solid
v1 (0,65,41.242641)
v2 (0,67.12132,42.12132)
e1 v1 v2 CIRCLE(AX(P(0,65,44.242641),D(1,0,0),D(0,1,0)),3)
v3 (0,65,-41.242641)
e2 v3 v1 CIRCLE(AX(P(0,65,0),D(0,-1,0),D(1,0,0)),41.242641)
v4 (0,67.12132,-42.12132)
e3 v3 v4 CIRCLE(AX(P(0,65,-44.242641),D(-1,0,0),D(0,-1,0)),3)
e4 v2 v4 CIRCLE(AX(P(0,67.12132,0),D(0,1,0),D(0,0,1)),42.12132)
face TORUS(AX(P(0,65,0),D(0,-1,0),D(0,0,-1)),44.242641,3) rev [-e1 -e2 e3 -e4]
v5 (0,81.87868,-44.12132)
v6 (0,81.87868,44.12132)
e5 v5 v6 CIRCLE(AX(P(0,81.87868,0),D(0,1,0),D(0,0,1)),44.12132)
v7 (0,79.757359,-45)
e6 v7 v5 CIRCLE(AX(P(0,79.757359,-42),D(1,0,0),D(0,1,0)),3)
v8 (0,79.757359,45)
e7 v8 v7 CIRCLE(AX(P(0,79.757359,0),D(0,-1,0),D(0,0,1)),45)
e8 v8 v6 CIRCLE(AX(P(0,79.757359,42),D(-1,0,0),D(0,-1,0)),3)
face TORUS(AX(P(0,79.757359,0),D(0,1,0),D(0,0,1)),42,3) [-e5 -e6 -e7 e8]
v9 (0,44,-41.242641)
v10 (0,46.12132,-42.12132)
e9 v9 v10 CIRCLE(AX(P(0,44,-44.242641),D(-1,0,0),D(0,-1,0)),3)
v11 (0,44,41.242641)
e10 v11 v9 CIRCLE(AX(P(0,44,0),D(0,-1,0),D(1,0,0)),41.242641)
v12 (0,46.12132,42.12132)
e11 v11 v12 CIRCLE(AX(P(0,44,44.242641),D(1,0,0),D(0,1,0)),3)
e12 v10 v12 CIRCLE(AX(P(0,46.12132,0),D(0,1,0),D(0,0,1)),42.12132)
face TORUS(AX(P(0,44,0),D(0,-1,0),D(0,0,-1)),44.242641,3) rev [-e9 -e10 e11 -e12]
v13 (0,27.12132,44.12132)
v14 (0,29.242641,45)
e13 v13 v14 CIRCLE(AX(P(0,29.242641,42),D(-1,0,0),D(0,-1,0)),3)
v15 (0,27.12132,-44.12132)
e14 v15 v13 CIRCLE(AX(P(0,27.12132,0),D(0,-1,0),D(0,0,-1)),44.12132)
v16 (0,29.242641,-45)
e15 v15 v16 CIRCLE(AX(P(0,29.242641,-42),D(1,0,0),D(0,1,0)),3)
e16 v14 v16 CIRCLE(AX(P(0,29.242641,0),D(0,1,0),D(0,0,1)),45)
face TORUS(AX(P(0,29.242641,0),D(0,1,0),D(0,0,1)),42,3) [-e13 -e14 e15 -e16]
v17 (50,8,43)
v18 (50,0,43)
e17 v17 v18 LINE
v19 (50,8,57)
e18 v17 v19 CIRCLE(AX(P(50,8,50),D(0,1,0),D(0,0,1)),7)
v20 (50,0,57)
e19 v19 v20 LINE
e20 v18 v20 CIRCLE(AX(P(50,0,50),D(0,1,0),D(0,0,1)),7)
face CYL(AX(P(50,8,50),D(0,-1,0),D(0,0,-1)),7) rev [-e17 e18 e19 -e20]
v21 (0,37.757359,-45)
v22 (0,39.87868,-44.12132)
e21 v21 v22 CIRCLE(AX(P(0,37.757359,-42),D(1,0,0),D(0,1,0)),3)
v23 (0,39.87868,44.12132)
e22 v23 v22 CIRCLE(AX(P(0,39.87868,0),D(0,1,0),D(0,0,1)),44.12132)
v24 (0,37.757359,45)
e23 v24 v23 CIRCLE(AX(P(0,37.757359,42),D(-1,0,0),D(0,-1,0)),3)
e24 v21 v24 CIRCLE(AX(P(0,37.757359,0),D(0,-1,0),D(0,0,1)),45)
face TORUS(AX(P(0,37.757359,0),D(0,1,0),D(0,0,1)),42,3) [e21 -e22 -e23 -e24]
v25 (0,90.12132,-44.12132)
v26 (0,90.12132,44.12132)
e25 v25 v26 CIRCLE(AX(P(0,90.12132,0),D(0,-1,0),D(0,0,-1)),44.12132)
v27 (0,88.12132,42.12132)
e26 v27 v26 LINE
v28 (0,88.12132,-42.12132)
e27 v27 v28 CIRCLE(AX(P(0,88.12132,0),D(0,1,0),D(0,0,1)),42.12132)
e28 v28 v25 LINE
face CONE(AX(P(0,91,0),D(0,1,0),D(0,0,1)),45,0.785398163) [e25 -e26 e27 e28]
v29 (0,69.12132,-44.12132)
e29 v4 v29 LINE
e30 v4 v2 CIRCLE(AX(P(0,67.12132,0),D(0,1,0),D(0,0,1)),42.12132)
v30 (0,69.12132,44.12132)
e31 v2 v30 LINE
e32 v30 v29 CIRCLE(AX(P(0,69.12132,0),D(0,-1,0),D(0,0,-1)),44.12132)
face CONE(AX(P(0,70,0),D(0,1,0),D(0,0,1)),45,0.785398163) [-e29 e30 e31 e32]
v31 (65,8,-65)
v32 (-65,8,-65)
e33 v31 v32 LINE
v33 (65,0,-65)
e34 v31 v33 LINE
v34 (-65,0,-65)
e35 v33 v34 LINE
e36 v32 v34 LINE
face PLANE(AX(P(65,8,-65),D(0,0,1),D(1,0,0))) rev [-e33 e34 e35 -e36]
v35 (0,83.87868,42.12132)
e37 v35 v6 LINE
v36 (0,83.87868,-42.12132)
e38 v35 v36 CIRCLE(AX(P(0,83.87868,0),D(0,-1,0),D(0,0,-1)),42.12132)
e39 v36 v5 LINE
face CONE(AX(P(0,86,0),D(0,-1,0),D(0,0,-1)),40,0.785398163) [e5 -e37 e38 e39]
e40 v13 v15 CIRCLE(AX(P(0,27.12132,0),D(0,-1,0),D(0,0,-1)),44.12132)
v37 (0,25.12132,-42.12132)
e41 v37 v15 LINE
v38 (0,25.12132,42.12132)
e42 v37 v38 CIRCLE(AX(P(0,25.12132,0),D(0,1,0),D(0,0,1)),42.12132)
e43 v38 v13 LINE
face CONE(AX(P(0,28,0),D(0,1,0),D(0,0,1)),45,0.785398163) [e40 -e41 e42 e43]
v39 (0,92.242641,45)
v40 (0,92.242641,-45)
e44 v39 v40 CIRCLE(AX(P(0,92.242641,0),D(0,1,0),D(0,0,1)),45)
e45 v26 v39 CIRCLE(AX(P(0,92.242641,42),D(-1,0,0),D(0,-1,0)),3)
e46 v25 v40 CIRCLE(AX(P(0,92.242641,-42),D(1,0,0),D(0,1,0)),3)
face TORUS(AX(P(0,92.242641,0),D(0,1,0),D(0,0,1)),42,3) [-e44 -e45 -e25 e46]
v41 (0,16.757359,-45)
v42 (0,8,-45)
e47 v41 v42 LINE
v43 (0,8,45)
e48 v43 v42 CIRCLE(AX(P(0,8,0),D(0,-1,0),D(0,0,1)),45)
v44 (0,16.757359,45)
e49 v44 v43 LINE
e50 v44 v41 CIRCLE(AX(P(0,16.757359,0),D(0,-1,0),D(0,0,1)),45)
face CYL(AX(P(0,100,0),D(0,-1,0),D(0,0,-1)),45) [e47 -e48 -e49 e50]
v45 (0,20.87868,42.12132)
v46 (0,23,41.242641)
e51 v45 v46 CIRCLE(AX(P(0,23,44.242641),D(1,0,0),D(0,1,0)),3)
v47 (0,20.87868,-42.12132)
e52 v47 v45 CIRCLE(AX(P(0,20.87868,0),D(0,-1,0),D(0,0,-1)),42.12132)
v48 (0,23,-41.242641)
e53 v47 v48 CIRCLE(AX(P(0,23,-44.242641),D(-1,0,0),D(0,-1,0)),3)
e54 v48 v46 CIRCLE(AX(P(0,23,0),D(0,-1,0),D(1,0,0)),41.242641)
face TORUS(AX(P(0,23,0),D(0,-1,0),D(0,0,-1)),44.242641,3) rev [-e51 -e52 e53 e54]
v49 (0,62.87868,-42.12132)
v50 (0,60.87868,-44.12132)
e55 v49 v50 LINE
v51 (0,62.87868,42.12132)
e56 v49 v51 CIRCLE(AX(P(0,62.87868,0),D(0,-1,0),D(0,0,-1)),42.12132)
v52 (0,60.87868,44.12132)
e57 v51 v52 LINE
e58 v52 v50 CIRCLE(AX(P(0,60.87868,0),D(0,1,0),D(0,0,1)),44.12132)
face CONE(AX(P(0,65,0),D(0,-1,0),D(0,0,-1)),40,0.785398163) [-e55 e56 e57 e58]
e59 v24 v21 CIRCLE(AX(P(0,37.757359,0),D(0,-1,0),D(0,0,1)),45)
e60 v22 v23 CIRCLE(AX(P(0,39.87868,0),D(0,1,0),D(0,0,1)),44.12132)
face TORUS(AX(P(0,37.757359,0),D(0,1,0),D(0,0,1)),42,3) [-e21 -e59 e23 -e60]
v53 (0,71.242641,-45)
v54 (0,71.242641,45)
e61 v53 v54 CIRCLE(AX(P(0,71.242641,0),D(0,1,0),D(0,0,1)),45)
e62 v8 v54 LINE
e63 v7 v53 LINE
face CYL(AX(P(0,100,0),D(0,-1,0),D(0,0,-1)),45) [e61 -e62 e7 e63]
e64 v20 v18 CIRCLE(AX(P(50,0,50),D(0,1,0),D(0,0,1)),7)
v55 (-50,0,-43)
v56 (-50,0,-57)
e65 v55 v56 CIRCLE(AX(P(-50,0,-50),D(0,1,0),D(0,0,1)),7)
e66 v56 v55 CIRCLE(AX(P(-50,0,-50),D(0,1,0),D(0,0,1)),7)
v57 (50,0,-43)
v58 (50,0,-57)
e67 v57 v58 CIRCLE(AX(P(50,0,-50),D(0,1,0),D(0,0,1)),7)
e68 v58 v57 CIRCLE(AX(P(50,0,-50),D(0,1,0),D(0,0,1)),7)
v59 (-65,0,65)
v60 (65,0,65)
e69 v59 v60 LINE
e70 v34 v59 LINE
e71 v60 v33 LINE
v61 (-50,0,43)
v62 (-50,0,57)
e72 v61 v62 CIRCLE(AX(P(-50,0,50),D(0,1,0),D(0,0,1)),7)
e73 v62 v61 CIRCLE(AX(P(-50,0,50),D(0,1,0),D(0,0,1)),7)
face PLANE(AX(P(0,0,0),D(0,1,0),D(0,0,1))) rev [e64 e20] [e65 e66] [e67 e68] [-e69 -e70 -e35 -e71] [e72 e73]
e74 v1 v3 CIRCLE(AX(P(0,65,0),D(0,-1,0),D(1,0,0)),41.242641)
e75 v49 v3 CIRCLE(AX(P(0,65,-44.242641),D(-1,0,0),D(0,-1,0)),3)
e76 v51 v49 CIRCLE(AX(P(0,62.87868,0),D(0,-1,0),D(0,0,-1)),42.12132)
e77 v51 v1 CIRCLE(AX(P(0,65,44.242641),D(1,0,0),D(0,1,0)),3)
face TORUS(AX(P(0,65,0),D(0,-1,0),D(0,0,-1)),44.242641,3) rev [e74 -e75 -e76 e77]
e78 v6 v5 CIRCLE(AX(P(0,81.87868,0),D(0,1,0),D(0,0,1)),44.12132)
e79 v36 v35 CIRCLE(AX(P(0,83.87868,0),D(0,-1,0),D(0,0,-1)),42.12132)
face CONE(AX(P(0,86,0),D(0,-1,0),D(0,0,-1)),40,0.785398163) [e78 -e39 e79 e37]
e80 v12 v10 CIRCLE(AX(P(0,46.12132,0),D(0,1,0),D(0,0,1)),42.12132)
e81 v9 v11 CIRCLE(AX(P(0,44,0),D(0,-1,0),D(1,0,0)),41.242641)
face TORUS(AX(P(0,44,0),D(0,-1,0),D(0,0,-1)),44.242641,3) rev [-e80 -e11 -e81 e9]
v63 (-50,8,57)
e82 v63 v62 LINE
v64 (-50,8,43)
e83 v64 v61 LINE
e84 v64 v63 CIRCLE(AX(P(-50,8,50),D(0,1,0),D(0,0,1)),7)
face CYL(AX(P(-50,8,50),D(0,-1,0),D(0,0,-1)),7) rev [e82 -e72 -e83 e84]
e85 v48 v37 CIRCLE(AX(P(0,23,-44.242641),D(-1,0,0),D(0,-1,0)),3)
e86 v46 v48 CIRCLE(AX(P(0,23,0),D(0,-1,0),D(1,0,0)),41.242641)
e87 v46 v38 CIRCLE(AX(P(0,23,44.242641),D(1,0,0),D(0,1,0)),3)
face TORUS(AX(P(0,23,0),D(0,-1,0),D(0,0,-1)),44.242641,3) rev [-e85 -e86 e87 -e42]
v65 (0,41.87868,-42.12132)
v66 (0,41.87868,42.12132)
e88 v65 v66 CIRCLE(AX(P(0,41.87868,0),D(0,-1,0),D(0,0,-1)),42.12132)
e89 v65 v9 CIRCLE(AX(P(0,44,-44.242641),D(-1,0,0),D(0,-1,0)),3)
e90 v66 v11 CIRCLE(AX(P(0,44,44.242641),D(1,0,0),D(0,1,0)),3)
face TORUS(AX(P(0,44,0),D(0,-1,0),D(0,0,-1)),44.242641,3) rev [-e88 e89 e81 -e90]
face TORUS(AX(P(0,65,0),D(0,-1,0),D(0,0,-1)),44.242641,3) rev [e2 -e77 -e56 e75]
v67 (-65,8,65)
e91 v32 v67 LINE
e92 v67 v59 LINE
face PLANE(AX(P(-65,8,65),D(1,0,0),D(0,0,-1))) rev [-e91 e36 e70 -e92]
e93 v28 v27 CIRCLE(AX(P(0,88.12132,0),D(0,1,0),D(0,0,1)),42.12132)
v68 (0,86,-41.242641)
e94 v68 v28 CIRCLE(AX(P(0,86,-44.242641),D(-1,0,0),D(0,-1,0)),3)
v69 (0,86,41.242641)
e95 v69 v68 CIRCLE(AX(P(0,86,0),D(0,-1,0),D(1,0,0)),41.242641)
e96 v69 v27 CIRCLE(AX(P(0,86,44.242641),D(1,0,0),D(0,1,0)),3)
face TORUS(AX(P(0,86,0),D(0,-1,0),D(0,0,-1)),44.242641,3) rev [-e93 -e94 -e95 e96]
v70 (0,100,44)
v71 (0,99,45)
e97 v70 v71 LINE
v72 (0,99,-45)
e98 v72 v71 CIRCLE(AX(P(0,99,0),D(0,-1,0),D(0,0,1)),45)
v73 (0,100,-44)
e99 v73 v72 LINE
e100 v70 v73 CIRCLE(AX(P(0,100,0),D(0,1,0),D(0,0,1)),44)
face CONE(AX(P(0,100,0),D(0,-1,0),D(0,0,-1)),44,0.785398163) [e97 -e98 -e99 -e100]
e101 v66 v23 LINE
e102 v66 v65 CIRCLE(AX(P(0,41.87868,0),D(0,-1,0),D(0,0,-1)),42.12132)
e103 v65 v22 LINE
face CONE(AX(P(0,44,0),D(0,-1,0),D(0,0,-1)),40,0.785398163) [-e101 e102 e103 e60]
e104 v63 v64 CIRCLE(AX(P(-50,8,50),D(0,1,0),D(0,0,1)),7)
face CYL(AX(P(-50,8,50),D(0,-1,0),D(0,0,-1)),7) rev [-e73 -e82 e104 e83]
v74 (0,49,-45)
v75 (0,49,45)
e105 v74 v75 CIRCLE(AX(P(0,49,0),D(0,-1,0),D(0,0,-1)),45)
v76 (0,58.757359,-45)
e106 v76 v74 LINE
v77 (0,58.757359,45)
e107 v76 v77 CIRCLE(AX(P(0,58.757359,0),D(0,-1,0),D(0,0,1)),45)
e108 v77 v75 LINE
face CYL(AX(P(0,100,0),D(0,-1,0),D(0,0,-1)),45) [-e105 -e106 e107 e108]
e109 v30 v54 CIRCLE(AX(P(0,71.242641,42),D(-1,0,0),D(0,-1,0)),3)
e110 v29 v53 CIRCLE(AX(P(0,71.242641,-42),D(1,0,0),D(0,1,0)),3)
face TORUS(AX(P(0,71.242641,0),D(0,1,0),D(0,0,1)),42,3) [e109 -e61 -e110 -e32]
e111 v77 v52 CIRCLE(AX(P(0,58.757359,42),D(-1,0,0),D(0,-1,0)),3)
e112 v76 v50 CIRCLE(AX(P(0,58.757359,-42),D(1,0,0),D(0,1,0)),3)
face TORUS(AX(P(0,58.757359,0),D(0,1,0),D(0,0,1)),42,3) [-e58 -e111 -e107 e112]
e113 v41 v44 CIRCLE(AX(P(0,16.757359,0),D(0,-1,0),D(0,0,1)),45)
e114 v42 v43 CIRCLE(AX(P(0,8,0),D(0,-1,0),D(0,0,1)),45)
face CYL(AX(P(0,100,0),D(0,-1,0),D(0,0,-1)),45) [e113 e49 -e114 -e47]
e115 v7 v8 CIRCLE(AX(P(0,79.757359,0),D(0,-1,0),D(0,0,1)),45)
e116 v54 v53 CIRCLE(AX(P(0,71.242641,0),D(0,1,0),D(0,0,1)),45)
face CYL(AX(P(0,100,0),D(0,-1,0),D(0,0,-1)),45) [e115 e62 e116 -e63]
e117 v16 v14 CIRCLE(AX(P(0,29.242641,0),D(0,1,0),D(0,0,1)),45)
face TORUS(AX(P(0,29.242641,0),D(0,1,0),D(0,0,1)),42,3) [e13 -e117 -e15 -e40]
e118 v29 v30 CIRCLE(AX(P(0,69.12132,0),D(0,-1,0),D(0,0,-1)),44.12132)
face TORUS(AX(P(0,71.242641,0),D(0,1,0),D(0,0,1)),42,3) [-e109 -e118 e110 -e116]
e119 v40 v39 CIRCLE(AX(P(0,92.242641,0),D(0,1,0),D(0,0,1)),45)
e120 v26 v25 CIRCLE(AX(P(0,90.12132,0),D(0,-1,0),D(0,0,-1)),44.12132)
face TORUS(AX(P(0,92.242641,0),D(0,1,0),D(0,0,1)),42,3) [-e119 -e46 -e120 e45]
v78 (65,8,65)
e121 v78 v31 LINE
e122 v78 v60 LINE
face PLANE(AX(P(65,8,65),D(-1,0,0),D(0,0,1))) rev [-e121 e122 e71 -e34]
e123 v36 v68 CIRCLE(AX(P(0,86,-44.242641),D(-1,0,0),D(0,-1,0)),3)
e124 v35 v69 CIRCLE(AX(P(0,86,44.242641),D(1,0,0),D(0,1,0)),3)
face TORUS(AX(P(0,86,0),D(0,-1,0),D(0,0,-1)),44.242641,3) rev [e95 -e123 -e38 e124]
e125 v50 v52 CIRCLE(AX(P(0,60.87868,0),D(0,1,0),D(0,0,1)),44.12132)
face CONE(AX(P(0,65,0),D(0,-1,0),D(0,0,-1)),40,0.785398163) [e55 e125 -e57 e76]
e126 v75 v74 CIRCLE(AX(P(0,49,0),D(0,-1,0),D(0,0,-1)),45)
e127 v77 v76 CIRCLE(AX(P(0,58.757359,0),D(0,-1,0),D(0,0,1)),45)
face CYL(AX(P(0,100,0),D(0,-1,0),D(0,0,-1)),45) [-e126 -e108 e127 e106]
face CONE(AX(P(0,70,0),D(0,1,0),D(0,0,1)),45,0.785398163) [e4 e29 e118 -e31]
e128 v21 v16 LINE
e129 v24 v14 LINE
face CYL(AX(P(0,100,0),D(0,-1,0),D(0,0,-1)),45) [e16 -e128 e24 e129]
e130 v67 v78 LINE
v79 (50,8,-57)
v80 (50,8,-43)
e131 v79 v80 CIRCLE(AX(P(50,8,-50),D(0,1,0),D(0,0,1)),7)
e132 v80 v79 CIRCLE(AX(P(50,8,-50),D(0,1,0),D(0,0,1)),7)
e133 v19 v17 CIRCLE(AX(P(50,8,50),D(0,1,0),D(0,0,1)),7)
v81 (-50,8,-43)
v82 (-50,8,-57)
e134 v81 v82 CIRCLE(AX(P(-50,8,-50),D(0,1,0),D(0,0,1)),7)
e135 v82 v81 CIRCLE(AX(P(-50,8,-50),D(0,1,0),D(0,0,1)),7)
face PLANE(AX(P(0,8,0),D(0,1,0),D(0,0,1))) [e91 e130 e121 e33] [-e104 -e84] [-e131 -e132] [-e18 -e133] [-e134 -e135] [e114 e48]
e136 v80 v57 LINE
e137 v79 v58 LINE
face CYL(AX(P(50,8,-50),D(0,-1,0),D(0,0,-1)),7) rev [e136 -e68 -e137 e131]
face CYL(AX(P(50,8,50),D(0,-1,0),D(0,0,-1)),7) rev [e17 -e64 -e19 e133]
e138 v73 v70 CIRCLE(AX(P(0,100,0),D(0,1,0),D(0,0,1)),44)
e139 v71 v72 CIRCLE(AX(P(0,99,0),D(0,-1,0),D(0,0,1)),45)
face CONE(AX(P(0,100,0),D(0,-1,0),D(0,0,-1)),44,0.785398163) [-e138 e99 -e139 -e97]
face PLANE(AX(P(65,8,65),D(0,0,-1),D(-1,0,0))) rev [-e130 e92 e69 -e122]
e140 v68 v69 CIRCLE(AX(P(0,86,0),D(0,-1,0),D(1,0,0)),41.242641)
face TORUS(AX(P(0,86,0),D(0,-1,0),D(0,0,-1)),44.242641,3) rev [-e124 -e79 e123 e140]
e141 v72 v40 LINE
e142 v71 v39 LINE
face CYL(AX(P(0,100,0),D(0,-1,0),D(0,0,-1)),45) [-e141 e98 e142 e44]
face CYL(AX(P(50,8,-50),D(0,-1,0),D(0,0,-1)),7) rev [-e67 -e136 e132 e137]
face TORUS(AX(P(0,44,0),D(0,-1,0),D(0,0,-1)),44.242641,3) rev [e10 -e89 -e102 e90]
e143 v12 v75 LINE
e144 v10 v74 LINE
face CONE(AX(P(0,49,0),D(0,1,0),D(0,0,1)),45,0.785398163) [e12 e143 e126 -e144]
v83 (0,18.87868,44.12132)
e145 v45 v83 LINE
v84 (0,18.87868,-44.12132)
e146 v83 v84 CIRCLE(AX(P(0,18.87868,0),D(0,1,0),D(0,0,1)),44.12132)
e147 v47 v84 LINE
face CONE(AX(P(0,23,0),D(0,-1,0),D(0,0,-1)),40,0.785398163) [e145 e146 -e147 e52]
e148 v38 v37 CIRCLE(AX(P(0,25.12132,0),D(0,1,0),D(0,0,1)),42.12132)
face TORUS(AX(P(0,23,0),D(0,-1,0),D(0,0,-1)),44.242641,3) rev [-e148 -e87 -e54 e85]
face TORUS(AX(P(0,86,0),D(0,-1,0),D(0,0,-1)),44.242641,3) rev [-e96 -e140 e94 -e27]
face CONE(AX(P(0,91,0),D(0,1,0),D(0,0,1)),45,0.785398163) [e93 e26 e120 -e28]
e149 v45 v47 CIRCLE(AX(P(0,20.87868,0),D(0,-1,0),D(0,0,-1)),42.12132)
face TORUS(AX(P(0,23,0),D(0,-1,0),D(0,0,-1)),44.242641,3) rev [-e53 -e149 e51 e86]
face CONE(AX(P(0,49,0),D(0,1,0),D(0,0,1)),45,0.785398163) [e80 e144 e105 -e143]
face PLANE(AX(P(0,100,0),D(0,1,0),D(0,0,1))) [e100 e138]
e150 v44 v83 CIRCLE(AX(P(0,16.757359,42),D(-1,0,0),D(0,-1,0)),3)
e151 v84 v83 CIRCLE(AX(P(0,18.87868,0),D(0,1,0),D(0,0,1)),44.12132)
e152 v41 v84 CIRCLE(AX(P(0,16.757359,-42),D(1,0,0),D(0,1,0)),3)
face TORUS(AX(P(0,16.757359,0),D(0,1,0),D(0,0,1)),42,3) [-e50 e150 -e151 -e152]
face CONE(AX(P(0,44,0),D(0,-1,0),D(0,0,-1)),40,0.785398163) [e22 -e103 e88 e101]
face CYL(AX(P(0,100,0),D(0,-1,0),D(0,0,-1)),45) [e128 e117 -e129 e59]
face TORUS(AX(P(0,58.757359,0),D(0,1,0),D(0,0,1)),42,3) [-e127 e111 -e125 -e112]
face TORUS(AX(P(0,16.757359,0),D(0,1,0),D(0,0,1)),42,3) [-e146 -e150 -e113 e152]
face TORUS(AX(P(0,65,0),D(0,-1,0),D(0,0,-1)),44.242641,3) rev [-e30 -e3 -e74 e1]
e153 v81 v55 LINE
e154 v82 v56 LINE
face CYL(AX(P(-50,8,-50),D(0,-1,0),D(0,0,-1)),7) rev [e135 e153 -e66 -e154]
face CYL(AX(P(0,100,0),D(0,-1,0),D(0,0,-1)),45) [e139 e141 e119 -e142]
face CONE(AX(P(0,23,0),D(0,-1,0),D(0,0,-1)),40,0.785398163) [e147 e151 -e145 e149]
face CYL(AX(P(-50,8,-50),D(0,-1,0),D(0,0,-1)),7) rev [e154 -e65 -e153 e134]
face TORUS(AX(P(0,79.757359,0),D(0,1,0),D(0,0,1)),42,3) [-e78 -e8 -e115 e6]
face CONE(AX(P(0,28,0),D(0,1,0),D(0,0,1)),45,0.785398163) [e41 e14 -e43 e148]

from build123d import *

# Parameters (mm, degrees)
SKETCH2_W           = 130
SKETCH2_H           = 130
SKETCH2_R           = 7
BOSS_EXTRUDE1_DEPTH = 8
SKETCH3_R           = 45
BOSS_EXTRUDE2_DEPTH = 100
CHAMFER1_SIZE       = 1
FILLET1_R           = 3


with BuildPart() as part:
    # Sketch2 → Boss-Extrude1 (new body)
    with BuildSketch(Plane(origin=(0, 0, 0), x_dir=(1, 0, 0), z_dir=(0, 1, 0))):
        Rectangle(SKETCH2_W, SKETCH2_H)
        with Locations(Location((-50, -50, 0), (0, 0, 270))):
            Circle(SKETCH2_R, mode=Mode.SUBTRACT)
        with Locations(Location((-50, 50, 0), (0, 0, 270))):
            Circle(SKETCH2_R, mode=Mode.SUBTRACT)
        with Locations(Location((50, 50, 0), (0, 0, 270))):
            Circle(SKETCH2_R, mode=Mode.SUBTRACT)
        with Locations(Location((50, -50, 0), (0, 0, 270))):
            Circle(SKETCH2_R, mode=Mode.SUBTRACT)
    extrude(amount=BOSS_EXTRUDE1_DEPTH)

    # Sketch3 → Boss-Extrude2 (add)
    with BuildSketch(Plane(origin=(0, 0, 0), x_dir=(1, 0, 0), z_dir=(0, 1, 0))):
        with Locations(Location((0, 0, 0), (0, 0, 270))):
            Circle(SKETCH3_R)
    extrude(amount=BOSS_EXTRUDE2_DEPTH)

    # Chamfer1
    chamfer1_edges = [part.edges().sort_by_distance(p)[0] for p in [
        (0, 100, -45),
    ]]
    chamfer(chamfer1_edges, length=CHAMFER1_SIZE)

    # Sketch4 → Cut-Revolve1 (revolve, cut)
    with BuildSketch(Plane.XY, mode=Mode.PRIVATE) as cut_revolve1_sk:
        Polygon((45, 18), (40, 23), (45, 28), align=None)
        Polygon((45, 39), (40, 44), (45, 49), align=None)
        Polygon((45, 60), (40, 65), (45, 70), align=None)
        Polygon((45, 81), (40, 86), (45, 91), align=None)
    revolve(cut_revolve1_sk.sketch.rotate(Axis((0, 0, 0), (0, 1, 0)), 90), axis=Axis((0, 0, 0), (0, 1, 0)), mode=Mode.SUBTRACT)

    # Fillet1
    fillet1_edges = [part.edges().sort_by_distance(p)[0] for p in [
        (-45, 28, 0),
        (-45, 18, 0),
        (0, 23, 40),
        (-45, 39, 0),
        (0, 44, 40),
        (-45, 70, 0),
        (-45, 60, 0),
        (0, 65, 40),
        (-45, 91, 0),
        (-45, 81, 0),
        (0, 86, 40),
    ]]
    fillet(fillet1_edges, radius=FILLET1_R)


solid = part.part
